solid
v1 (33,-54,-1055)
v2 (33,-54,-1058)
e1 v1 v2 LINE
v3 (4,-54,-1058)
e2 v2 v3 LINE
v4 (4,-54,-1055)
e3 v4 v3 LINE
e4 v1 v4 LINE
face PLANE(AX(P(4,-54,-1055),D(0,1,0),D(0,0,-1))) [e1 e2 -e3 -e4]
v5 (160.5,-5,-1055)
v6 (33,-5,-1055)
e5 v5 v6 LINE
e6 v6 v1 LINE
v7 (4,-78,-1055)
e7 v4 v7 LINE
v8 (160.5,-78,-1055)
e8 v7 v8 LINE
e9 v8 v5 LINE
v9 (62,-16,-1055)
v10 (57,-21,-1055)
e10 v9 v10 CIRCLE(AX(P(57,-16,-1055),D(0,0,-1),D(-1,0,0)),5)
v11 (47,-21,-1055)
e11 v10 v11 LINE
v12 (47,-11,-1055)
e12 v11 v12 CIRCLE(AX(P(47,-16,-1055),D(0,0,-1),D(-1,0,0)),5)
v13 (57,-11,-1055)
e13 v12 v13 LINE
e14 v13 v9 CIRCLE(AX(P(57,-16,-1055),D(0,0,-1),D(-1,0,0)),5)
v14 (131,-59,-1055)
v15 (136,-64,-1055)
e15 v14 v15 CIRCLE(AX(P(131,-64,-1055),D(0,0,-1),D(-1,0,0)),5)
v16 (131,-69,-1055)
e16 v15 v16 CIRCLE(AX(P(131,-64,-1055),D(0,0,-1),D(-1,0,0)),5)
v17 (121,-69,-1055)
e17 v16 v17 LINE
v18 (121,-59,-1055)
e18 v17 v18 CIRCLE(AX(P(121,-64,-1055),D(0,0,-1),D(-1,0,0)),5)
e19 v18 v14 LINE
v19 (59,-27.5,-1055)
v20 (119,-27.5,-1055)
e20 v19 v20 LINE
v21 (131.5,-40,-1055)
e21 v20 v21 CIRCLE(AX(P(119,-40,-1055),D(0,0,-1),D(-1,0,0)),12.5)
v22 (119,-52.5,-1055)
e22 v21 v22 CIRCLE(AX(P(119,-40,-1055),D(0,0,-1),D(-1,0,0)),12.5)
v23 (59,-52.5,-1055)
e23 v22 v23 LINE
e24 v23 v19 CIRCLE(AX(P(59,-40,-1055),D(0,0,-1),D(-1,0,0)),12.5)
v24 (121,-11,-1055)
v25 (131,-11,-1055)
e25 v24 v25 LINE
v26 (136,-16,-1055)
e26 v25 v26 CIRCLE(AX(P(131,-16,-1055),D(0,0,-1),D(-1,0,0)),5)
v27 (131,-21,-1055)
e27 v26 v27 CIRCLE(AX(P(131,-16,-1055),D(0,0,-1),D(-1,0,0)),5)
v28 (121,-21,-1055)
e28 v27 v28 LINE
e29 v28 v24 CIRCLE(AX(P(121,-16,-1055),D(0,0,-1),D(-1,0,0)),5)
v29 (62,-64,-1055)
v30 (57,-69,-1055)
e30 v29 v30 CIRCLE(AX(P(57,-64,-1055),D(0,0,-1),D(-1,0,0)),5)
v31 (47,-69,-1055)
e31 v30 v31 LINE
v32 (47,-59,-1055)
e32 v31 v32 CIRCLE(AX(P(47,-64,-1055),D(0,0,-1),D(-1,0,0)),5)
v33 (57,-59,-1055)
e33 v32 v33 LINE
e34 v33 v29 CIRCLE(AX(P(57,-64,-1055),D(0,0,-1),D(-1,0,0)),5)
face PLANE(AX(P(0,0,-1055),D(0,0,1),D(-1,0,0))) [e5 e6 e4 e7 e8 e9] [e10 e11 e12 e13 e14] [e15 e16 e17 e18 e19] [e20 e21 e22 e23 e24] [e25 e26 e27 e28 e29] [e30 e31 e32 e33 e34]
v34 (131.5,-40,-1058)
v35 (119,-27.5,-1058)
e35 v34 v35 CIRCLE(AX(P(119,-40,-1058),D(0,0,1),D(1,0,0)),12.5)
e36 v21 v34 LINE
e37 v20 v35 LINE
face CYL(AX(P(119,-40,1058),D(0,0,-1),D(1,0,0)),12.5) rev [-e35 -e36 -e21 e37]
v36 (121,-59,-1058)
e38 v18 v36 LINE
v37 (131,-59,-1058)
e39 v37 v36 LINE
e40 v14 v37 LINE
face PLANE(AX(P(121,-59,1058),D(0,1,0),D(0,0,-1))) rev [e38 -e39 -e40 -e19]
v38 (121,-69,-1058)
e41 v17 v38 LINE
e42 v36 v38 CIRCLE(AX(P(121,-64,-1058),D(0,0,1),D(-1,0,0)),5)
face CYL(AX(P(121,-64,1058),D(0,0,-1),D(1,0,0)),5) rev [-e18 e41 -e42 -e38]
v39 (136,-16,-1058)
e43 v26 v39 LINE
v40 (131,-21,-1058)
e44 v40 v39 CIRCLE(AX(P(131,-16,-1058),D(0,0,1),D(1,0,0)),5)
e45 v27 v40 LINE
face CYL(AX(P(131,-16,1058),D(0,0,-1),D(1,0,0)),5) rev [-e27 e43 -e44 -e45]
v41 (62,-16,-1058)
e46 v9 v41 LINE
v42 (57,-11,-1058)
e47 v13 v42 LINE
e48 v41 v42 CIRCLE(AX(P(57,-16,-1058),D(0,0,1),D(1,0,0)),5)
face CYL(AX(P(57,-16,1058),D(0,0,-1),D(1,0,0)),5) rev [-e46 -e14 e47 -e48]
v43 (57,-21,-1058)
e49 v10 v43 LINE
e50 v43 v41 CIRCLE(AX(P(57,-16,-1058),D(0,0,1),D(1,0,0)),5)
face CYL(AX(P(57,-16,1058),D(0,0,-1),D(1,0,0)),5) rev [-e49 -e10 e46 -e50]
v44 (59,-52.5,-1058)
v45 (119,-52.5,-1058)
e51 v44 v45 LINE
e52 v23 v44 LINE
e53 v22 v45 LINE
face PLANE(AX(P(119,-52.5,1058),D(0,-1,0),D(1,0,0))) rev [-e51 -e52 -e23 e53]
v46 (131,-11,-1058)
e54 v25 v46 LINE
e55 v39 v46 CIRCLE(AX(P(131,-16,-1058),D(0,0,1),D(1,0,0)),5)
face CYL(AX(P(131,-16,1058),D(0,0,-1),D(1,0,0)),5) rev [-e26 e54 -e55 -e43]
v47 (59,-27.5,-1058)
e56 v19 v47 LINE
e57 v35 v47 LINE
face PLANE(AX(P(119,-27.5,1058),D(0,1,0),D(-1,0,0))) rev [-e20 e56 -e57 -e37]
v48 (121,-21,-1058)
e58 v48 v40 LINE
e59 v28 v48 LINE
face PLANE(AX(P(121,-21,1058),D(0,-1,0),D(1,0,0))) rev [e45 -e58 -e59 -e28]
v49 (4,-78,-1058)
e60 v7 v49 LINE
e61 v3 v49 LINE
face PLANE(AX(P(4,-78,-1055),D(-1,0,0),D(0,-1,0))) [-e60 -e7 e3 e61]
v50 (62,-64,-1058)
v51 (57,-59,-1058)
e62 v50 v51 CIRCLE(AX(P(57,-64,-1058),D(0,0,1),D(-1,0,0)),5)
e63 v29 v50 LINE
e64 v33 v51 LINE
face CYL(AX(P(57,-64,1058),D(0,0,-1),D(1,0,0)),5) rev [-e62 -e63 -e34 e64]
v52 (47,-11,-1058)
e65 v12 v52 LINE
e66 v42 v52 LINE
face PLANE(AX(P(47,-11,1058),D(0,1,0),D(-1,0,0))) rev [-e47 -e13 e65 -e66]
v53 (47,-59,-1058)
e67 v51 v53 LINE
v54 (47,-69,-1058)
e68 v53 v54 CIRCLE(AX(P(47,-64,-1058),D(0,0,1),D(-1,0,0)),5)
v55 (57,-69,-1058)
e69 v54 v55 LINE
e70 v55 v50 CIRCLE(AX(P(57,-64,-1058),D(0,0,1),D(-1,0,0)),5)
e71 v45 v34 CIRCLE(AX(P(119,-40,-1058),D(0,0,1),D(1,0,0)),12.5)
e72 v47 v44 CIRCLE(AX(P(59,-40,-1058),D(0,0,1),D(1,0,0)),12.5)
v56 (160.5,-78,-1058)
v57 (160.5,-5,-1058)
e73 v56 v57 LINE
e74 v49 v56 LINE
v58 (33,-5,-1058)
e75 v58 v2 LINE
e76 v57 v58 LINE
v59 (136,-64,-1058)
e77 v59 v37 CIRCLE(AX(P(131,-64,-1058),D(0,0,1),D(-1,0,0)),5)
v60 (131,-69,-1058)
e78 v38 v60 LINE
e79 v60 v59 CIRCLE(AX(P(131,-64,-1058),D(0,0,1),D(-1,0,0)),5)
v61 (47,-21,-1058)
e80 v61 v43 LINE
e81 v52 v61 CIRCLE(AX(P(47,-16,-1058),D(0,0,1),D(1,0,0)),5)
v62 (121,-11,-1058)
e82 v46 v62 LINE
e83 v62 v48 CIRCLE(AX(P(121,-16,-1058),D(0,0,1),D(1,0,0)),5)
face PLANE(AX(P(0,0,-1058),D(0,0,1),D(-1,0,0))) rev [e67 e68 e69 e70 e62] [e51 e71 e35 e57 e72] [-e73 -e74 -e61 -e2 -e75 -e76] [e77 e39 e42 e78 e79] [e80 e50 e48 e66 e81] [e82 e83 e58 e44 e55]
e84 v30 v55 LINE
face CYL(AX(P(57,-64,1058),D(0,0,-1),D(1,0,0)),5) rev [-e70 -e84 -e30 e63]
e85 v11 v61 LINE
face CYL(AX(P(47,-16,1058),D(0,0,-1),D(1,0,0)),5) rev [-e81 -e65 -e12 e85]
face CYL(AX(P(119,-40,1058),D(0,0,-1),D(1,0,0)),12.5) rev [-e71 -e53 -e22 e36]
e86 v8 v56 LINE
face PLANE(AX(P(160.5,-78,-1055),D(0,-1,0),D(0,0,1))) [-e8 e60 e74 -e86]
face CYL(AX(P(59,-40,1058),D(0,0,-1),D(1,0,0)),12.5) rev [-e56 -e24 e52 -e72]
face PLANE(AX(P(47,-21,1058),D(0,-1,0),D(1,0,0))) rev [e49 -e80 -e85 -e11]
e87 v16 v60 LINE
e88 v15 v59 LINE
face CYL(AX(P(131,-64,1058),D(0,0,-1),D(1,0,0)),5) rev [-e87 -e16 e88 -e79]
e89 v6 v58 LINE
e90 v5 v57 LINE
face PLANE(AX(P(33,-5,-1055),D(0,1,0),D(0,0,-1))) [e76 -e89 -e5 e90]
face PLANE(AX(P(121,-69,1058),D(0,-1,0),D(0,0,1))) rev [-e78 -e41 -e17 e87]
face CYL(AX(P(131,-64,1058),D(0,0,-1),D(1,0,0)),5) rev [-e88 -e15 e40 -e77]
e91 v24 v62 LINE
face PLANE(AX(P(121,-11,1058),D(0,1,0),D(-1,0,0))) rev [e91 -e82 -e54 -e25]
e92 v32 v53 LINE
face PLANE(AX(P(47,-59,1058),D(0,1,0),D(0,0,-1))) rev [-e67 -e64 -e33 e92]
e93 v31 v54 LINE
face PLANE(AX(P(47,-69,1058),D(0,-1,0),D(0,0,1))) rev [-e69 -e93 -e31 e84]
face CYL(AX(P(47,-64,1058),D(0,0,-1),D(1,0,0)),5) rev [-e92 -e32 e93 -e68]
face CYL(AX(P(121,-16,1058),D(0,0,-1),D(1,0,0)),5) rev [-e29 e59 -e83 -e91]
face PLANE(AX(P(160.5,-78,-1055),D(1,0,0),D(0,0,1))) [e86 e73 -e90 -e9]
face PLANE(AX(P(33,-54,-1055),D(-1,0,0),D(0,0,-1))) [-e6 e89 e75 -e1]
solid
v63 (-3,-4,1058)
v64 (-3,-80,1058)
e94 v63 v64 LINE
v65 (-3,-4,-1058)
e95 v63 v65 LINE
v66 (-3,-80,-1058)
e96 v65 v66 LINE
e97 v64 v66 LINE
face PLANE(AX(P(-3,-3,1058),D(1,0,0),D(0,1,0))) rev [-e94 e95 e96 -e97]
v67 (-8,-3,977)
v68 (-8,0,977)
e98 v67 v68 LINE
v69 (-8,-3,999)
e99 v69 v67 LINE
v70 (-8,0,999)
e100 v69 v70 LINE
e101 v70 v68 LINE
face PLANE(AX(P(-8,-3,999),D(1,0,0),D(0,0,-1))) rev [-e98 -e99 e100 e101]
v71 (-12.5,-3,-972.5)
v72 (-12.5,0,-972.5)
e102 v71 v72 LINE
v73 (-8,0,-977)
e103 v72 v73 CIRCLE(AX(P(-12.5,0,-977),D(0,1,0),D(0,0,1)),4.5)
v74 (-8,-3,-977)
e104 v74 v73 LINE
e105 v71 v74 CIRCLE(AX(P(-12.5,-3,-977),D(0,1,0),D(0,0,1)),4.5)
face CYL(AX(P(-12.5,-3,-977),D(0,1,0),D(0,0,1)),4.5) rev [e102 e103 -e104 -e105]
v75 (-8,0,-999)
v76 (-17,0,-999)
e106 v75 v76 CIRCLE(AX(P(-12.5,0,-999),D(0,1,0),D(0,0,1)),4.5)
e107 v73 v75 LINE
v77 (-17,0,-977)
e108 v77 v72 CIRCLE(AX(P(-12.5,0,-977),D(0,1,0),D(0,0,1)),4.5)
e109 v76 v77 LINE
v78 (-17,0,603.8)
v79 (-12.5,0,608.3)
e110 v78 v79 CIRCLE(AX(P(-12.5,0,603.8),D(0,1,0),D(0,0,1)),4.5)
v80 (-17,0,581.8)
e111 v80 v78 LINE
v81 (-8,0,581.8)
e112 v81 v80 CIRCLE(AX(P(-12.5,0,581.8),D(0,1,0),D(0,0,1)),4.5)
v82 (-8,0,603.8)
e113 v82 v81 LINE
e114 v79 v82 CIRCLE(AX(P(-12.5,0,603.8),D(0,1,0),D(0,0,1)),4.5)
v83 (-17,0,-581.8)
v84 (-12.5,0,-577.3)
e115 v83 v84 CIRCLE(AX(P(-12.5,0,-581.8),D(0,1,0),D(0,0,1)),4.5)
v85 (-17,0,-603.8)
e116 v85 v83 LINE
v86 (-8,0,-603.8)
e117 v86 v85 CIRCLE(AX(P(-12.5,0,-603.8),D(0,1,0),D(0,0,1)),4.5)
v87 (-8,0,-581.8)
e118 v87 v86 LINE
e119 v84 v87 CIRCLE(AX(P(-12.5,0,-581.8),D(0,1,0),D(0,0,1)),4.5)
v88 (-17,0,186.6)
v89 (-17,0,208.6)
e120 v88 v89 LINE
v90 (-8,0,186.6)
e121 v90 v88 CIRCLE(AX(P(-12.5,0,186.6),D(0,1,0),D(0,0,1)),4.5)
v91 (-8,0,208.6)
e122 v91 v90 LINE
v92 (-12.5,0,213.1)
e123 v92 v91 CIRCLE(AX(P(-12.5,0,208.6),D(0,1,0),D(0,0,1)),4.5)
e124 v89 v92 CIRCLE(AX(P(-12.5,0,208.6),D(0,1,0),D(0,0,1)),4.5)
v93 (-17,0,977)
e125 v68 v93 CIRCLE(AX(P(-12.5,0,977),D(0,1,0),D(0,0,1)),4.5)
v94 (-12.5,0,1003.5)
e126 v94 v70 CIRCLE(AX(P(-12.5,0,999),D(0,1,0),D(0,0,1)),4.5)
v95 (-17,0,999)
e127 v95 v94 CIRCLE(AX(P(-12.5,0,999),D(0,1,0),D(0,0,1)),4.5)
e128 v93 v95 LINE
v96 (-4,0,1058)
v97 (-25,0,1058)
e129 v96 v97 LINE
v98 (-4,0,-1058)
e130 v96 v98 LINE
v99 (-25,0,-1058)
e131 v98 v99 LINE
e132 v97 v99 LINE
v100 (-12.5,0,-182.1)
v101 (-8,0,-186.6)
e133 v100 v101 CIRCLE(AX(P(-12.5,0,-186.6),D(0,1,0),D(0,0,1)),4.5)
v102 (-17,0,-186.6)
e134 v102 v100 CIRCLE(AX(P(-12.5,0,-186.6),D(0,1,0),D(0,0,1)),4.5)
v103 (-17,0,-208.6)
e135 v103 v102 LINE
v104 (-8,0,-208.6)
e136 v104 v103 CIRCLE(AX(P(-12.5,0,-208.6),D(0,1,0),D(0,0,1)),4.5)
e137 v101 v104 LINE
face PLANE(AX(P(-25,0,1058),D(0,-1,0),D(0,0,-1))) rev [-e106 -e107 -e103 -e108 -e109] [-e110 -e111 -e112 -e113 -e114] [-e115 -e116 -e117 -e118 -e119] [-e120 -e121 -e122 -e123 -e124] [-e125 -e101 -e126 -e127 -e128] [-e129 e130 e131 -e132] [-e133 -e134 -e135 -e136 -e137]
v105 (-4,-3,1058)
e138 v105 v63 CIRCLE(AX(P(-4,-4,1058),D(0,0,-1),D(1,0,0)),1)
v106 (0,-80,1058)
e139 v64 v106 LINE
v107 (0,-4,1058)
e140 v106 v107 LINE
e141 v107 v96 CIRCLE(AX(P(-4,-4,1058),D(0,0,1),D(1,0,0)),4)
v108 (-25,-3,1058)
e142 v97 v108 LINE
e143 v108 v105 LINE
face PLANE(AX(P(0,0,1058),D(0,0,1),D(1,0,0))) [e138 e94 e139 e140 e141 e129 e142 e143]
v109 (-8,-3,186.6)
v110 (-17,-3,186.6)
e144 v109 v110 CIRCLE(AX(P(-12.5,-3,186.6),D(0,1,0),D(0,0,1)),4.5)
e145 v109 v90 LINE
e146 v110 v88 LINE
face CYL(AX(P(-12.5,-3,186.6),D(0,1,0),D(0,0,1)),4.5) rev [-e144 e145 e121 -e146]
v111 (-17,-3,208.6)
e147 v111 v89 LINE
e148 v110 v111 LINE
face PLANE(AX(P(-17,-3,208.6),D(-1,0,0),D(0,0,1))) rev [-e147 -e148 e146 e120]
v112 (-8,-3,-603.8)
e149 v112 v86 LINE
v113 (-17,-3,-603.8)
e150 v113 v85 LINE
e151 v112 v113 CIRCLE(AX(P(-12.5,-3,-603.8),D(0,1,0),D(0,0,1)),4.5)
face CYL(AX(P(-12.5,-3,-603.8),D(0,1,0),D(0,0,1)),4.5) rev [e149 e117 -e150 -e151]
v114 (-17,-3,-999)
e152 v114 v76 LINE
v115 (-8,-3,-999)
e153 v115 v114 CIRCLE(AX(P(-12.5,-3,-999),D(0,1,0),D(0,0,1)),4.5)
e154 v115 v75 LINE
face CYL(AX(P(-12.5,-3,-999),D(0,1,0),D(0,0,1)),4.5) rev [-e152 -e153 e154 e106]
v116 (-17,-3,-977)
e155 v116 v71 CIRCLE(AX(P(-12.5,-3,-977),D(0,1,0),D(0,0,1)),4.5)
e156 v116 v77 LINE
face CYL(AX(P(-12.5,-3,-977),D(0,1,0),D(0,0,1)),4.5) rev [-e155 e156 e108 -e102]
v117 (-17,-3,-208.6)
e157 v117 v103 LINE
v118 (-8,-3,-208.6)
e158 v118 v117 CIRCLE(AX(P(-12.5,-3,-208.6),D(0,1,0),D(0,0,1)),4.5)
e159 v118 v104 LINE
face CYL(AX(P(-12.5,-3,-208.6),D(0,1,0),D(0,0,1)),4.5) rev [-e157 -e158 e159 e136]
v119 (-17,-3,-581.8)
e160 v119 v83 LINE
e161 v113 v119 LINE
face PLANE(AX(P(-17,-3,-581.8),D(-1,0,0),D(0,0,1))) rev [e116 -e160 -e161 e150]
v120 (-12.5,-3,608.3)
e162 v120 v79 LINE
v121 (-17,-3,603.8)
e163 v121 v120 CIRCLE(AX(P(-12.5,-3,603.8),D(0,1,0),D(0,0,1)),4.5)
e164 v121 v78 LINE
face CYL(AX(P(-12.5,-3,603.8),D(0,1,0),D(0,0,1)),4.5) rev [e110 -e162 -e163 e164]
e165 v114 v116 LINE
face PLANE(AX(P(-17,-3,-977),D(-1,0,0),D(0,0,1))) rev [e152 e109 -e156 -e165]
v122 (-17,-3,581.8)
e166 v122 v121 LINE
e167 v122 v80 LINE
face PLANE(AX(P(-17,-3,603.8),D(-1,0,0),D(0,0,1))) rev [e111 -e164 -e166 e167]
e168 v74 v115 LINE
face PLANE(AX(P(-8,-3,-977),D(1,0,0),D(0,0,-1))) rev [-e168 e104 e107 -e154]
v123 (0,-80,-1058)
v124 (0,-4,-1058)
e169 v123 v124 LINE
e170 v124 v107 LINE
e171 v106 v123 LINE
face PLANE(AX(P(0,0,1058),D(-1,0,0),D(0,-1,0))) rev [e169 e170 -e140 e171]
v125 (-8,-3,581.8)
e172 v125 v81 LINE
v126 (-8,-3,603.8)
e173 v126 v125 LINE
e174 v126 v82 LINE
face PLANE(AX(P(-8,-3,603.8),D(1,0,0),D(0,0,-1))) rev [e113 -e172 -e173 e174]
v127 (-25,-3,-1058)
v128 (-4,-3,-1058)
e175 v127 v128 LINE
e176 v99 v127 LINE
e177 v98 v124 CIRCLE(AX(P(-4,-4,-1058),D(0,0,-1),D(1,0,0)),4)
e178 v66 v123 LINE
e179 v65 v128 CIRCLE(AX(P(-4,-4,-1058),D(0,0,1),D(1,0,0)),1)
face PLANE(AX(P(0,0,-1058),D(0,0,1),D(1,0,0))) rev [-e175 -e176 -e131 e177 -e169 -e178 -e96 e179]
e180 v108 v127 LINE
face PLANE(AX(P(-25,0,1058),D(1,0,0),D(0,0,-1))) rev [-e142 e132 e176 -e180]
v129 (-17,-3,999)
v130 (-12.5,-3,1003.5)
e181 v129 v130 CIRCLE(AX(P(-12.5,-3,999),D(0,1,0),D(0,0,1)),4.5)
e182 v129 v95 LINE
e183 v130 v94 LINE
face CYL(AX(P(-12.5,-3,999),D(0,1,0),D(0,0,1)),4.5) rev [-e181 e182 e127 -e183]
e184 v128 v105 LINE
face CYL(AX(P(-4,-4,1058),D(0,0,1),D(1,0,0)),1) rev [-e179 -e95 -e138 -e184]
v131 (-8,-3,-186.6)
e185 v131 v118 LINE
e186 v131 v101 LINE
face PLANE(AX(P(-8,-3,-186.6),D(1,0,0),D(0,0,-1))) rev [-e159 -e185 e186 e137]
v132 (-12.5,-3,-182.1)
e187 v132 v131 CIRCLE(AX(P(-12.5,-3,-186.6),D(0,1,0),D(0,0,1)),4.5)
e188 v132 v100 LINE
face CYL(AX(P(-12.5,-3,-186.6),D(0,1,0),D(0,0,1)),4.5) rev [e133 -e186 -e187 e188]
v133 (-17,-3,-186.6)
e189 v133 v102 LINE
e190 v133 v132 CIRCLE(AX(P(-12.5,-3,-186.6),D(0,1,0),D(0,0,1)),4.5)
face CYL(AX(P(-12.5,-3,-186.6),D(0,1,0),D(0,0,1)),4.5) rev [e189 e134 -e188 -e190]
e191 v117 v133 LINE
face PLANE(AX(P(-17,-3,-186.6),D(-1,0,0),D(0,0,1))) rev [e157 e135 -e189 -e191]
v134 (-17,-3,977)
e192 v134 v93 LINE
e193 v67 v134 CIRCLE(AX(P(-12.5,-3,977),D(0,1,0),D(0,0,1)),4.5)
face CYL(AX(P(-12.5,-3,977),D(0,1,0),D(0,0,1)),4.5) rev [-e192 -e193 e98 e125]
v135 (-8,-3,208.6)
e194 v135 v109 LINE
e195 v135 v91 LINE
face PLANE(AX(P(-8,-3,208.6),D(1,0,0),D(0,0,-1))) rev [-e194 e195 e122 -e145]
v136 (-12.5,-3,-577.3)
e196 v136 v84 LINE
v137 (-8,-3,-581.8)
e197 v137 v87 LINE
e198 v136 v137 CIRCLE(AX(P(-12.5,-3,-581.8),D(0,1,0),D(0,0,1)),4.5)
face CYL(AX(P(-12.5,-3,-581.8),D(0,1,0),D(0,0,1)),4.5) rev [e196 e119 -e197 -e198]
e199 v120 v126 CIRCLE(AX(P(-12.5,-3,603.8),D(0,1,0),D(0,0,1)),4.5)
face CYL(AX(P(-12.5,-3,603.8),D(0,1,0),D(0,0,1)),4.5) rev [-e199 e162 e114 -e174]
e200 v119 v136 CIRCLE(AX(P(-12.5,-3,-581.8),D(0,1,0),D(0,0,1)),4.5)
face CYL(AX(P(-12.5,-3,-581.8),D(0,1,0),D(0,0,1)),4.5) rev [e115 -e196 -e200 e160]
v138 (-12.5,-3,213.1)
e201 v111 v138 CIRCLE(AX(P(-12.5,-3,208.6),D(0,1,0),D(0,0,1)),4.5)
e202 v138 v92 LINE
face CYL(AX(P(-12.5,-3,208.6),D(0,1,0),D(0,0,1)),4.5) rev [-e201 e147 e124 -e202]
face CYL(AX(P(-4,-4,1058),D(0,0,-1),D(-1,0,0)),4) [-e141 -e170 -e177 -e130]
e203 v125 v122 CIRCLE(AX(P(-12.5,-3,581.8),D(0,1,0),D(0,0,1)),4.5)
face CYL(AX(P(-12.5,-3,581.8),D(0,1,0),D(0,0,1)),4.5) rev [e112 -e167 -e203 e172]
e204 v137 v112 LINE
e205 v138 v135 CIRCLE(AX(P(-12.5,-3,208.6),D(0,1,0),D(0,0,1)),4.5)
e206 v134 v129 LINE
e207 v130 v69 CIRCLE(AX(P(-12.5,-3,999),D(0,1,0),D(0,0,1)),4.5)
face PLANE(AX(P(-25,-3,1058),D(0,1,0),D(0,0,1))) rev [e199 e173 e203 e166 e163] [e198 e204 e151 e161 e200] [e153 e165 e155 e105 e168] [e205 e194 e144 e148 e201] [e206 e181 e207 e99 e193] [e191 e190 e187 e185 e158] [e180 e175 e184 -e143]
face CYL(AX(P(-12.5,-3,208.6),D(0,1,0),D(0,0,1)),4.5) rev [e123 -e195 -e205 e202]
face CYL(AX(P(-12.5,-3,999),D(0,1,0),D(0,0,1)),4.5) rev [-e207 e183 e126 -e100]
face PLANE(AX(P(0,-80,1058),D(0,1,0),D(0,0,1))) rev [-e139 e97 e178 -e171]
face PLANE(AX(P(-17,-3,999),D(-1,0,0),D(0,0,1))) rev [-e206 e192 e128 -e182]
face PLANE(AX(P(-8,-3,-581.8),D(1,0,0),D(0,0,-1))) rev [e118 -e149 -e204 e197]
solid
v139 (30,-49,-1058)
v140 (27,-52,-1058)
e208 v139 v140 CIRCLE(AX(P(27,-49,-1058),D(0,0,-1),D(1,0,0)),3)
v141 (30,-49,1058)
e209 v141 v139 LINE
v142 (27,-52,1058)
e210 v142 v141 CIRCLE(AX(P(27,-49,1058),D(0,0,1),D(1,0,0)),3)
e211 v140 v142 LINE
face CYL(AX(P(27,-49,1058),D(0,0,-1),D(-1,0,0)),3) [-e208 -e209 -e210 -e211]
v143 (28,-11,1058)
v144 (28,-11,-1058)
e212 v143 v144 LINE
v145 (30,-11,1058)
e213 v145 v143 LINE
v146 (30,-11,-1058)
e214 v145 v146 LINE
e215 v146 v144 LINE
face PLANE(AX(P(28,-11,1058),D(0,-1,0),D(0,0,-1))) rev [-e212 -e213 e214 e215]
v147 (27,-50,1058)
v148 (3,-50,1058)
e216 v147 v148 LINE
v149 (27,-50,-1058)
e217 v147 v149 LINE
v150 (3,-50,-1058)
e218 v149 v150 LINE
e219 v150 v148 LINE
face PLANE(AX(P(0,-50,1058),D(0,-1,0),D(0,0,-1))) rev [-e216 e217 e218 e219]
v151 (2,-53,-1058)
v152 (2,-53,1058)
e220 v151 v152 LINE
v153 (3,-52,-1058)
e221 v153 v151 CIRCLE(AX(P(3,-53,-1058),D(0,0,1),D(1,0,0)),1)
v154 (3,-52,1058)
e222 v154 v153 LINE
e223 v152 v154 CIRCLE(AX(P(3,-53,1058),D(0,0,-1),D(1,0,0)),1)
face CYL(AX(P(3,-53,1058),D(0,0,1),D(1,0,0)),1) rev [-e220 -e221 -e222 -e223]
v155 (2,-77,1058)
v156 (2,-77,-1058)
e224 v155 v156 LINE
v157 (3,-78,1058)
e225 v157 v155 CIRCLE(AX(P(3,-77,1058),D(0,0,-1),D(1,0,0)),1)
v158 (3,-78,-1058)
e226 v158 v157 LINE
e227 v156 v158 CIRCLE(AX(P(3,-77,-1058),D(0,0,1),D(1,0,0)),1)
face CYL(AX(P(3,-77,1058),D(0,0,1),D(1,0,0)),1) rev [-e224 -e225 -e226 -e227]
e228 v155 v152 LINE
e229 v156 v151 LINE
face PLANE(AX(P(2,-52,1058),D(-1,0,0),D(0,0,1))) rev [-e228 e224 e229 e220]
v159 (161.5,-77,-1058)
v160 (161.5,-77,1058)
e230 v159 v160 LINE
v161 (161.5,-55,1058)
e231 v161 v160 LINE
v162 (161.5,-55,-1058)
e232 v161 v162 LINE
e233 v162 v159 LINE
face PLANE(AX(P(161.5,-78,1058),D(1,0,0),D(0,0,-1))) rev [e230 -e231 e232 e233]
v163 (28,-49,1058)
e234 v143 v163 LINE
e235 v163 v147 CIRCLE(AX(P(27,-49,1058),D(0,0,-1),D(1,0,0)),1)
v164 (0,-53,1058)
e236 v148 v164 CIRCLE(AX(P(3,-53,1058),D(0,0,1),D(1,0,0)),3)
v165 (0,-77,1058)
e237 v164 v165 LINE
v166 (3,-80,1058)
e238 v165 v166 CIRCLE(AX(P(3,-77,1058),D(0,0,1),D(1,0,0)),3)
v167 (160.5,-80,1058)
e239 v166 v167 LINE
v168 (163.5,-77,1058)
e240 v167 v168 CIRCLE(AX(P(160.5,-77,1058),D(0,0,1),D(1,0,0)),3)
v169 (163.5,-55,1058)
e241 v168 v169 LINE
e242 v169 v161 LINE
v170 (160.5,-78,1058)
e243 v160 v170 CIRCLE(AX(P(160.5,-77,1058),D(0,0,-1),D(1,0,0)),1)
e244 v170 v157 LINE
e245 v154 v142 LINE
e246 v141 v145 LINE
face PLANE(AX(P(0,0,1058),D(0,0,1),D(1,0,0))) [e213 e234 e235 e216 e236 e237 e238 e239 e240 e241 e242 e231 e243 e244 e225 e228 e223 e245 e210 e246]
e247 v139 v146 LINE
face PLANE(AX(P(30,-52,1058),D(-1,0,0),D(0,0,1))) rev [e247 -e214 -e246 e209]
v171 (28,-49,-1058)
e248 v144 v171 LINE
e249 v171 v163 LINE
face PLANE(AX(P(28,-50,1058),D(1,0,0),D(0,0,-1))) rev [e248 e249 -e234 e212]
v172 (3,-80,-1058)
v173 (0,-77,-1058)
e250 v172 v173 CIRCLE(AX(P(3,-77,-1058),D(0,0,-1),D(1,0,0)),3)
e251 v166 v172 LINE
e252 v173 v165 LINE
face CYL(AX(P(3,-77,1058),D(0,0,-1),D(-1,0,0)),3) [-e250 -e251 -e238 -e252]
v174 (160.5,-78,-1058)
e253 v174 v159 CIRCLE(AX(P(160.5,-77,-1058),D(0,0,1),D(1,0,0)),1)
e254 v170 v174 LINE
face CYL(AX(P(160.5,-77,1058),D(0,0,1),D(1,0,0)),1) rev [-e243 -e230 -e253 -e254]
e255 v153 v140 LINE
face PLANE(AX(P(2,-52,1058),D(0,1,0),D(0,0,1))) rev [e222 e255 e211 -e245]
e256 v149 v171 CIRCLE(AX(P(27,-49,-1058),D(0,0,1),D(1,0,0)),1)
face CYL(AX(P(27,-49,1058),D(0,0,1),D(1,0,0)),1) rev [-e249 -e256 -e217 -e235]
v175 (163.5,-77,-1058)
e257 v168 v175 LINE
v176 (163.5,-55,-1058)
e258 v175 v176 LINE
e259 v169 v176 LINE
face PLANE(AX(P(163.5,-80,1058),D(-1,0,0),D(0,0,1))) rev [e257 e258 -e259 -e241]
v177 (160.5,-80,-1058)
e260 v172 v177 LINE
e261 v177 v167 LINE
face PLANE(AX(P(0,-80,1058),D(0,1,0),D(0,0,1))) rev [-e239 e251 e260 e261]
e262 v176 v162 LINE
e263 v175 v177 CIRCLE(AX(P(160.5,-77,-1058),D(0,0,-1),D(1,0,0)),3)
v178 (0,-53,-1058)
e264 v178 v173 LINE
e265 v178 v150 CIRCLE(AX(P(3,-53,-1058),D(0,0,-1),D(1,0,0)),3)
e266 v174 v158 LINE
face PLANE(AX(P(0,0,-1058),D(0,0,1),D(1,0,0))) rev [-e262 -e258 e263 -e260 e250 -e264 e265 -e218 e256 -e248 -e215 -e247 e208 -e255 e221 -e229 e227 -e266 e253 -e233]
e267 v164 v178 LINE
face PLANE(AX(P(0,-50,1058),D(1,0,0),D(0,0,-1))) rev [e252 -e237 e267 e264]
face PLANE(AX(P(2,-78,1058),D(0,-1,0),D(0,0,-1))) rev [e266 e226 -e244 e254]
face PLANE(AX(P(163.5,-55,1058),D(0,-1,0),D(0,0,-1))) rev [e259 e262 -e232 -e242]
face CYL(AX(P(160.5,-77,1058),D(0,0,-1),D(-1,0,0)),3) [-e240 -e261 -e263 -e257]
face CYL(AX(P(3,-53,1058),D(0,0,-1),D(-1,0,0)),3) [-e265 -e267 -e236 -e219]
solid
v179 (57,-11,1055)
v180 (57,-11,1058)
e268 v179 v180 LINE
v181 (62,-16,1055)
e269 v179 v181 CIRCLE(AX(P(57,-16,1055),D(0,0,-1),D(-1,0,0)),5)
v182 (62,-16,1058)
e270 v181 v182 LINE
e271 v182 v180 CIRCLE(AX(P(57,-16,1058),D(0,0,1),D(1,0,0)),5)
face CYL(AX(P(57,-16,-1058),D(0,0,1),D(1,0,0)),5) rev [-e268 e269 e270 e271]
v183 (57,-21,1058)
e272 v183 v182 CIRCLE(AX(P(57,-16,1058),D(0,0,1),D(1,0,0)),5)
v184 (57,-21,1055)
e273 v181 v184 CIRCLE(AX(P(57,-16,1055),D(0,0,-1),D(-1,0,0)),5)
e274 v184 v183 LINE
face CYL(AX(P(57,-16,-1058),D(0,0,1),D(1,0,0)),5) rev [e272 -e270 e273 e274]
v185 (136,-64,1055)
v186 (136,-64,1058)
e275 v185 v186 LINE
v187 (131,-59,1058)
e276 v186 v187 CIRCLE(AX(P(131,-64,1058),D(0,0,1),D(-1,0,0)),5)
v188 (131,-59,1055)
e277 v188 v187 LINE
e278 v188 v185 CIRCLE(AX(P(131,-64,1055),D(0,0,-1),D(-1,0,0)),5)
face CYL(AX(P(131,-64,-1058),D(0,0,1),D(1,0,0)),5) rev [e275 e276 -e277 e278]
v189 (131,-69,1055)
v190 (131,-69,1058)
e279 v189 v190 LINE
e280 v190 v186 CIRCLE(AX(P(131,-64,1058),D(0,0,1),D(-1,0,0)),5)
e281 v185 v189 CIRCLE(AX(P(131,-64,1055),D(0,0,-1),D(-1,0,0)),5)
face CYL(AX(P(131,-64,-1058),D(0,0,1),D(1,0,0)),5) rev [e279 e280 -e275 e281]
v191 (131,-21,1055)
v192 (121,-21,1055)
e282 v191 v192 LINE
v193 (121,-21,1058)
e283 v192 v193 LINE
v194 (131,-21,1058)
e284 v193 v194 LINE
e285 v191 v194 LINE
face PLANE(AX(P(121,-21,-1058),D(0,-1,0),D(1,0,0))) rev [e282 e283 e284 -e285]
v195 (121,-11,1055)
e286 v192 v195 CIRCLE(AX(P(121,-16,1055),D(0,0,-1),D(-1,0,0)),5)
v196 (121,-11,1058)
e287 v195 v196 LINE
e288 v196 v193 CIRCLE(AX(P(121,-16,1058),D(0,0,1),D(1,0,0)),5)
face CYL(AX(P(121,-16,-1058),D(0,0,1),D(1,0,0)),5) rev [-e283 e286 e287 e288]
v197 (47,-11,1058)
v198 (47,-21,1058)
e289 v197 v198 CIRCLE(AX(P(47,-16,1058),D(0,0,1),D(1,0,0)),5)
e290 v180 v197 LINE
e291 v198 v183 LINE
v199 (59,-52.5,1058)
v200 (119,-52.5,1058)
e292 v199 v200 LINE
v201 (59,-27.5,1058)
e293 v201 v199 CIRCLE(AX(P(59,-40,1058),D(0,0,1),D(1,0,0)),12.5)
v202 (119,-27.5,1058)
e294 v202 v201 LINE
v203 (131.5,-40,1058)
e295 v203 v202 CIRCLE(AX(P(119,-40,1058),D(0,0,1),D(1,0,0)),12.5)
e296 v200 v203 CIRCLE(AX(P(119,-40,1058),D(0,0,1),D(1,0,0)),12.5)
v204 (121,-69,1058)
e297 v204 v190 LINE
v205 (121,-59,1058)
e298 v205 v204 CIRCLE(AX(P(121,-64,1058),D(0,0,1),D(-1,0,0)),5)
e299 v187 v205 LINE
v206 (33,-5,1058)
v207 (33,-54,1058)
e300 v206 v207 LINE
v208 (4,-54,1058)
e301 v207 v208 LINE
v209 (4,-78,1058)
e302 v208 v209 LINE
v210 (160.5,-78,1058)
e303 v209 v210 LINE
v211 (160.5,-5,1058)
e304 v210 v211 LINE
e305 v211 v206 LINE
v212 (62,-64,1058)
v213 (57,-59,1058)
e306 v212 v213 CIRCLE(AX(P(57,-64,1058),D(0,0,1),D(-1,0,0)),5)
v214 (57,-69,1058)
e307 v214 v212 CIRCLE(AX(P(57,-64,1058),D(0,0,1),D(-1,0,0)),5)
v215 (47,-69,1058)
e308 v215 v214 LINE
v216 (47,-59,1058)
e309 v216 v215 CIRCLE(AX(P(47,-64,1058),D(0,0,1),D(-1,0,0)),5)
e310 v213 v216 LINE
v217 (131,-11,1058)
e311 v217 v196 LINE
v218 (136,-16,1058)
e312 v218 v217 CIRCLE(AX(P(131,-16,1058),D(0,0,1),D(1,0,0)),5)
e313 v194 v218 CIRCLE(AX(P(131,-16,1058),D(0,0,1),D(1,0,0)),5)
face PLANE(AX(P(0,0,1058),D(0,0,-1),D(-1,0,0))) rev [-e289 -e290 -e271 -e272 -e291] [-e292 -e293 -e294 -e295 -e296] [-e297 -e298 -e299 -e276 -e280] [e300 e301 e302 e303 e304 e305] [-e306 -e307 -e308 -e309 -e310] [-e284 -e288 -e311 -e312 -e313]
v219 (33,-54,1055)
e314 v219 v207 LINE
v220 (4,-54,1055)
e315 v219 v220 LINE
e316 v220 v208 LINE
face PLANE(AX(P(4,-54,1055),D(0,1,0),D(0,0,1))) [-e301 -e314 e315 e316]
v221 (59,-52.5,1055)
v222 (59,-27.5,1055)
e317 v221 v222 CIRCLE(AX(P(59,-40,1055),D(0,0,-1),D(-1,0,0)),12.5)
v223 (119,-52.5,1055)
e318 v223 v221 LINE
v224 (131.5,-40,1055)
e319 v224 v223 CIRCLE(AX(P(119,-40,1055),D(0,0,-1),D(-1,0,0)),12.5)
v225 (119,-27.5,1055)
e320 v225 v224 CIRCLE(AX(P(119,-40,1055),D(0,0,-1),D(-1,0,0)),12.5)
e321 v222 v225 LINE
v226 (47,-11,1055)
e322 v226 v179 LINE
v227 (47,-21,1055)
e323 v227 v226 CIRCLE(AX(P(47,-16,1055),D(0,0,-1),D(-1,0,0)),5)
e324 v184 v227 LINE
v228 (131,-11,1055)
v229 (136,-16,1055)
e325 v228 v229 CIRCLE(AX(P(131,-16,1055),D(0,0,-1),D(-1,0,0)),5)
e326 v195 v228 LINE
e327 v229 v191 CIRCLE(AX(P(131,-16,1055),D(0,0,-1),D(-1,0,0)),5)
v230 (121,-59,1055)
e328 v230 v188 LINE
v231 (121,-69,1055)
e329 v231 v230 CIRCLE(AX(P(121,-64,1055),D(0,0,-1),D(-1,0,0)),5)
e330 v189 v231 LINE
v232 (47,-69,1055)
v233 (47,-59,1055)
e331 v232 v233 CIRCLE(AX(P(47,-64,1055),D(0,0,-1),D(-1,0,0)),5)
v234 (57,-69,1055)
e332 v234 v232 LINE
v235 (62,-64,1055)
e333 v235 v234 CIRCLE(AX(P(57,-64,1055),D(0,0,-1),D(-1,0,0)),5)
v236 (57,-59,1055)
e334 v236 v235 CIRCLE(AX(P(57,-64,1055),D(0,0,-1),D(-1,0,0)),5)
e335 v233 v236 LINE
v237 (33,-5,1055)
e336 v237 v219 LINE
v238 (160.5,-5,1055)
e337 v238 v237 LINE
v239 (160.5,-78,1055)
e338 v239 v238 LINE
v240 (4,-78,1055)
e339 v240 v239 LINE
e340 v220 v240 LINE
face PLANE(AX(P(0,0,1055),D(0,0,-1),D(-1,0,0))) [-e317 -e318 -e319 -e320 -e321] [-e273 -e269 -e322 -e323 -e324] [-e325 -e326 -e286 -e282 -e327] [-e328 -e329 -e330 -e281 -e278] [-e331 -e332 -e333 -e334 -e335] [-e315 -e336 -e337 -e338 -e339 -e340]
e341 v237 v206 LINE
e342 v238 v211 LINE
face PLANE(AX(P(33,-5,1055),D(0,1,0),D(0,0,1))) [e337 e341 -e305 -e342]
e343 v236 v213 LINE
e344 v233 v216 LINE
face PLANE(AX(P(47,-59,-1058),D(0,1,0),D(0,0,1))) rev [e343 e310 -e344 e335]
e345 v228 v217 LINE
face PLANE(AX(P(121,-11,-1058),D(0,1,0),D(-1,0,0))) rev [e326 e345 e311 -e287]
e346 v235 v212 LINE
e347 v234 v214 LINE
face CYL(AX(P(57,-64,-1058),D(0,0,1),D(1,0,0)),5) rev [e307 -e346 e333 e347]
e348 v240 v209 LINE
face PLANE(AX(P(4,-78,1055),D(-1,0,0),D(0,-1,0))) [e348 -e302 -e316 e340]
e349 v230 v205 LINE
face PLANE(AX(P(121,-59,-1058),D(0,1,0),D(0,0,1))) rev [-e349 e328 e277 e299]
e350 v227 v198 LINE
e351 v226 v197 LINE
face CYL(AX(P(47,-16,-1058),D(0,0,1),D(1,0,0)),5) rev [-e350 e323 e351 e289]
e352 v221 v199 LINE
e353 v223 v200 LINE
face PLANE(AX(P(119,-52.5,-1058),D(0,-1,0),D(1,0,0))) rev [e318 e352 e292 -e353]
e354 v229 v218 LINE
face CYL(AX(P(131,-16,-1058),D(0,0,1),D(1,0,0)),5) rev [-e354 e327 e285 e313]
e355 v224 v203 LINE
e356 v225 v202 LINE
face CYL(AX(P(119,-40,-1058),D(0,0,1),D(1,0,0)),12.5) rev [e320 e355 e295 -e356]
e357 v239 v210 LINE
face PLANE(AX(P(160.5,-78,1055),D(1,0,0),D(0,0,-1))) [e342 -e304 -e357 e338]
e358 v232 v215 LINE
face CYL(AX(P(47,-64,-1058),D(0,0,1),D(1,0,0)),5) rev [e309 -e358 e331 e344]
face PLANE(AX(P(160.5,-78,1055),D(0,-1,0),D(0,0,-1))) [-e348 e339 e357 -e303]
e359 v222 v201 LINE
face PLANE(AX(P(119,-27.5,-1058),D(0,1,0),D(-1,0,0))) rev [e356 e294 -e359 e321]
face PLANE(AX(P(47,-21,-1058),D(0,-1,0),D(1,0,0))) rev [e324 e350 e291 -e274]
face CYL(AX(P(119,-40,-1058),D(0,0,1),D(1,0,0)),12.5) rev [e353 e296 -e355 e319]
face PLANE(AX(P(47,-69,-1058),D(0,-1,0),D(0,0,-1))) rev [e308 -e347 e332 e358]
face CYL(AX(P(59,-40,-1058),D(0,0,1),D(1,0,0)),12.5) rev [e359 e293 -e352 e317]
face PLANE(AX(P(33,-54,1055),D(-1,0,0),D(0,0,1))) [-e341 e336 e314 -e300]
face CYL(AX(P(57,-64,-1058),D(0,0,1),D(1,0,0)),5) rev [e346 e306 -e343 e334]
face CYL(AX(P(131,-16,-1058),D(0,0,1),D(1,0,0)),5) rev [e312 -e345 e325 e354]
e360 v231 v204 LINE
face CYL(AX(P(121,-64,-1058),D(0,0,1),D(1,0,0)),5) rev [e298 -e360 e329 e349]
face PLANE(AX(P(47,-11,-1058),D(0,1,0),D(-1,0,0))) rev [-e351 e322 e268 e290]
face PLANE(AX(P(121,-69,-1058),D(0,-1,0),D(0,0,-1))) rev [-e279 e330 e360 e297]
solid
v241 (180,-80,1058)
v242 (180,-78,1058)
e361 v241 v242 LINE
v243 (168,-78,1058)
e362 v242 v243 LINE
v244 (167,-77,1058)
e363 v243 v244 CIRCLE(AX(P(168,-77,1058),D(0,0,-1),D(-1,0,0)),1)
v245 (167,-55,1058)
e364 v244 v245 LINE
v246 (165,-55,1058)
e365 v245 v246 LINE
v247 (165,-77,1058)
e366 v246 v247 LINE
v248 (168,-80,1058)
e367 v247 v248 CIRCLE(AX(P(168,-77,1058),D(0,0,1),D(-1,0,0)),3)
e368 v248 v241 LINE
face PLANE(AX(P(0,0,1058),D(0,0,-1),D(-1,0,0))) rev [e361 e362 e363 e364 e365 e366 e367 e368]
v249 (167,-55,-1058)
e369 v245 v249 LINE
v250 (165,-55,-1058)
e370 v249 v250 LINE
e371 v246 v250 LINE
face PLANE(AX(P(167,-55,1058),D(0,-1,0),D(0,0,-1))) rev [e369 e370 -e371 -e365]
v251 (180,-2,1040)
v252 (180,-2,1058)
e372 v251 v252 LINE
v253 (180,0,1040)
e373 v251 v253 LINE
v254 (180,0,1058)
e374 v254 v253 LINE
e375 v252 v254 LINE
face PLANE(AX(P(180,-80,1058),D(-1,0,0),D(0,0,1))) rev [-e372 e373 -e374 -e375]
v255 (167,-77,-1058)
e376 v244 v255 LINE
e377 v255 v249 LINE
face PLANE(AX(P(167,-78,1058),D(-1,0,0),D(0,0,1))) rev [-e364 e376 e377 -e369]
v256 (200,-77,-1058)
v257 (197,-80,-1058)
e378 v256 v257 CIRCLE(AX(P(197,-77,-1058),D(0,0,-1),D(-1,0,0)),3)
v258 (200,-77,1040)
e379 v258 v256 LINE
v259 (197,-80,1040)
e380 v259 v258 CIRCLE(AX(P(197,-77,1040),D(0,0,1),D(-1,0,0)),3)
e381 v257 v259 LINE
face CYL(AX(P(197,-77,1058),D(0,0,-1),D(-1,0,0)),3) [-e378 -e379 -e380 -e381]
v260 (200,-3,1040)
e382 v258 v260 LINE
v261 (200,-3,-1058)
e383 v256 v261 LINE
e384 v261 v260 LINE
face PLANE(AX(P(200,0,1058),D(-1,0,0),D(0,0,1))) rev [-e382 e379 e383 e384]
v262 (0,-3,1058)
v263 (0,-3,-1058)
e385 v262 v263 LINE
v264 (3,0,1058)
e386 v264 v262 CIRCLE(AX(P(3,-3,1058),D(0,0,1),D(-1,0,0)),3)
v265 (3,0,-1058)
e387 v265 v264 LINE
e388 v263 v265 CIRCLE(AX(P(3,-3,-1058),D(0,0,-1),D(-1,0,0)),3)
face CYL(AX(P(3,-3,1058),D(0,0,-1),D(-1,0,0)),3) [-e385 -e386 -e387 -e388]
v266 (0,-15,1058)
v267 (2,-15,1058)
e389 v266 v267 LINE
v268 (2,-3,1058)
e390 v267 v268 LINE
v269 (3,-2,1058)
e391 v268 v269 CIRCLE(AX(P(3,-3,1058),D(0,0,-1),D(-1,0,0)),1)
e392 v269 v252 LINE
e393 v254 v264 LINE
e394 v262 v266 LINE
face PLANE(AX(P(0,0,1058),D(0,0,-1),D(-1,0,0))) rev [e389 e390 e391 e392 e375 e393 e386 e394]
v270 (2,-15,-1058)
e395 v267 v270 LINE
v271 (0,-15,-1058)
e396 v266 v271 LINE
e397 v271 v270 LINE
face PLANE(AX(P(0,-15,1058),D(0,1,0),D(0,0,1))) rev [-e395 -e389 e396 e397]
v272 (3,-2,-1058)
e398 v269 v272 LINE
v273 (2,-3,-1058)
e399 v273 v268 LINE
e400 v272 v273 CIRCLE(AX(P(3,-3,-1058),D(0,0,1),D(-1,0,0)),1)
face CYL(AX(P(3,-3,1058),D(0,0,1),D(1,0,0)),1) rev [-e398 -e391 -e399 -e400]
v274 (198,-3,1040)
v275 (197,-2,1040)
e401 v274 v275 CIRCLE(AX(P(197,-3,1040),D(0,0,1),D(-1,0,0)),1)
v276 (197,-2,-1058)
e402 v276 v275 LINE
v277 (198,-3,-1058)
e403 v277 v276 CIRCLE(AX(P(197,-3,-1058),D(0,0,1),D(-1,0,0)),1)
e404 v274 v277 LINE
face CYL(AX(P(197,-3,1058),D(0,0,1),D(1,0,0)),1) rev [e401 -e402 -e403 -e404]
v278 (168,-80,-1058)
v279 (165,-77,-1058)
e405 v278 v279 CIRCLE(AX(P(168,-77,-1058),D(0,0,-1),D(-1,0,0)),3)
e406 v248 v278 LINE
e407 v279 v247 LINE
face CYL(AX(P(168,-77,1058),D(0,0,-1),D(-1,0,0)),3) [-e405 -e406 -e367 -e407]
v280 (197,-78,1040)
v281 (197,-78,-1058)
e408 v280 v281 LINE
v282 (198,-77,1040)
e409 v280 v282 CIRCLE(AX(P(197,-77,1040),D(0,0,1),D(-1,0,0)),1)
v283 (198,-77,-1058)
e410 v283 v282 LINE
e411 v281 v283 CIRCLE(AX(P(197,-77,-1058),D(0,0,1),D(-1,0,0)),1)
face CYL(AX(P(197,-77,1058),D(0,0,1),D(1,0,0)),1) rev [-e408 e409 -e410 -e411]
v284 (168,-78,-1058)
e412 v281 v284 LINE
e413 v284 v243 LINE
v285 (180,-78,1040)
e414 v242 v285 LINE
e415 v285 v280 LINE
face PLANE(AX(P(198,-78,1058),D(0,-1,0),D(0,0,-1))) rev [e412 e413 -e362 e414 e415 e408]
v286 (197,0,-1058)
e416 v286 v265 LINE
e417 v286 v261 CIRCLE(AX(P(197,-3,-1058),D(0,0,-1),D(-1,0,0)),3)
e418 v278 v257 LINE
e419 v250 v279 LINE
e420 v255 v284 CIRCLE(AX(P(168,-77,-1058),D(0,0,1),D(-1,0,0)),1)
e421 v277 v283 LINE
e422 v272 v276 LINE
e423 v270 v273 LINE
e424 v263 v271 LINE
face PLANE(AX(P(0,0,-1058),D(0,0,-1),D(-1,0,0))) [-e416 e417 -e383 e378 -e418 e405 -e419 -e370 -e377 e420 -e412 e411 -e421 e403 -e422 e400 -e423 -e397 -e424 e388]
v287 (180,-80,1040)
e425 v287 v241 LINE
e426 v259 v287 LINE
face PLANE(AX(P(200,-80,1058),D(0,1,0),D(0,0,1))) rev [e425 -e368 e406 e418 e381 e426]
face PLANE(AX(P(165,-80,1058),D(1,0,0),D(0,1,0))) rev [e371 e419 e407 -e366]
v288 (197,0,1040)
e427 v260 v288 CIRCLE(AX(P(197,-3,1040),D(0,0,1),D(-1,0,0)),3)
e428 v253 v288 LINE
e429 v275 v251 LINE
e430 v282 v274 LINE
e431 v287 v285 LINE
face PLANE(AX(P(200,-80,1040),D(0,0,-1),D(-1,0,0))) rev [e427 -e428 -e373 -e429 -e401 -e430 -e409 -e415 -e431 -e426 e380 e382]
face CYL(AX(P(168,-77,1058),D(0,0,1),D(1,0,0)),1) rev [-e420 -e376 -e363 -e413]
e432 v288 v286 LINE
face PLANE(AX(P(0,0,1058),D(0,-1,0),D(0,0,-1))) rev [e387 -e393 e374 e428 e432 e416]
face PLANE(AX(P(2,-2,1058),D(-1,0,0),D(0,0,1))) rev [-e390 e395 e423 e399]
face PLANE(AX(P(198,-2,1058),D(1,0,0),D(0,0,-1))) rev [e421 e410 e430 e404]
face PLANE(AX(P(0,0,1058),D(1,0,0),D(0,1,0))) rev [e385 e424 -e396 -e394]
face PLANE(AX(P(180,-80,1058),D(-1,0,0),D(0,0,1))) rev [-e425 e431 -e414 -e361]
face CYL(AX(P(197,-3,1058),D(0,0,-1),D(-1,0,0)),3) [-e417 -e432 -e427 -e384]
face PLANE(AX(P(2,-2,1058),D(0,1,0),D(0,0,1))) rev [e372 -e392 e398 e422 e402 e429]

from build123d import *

# Parameters (mm, degrees)
EXTRUDE_1_DEPTH             = 1058
EXTRUDE_2_DEPTH             = 1058
EXTRUDE_2_2_DEPTH           = 1058
EXTRUDE_3_DEPTH             = 3
FILLET_1_R                  = 4
FILLET_2_R                  = 1
FILLET_3_R                  = 1
FILLET_4_R                  = 1
FILLET_5_R                  = 3
FILLET_6_R                  = 3
CUT_EXTRUDE_1_DEPTH         = 2127.935824138
CUT_EXTRUDE_3487_DEPTH      = 3
CUT_EXTRUDE_3708_DEPTH      = 1080.705515407
CUT_EXTRUDE_3708_DEPTH_BACK = 1080.705515407
SKETCH_6_W                  = 20
SKETCH_6_H                  = 18


with BuildPart() as part:
    # 草图1 → 凸台-拉伸1 (new, symmetric)
    with BuildSketch(Plane.XY):
        Polygon((-25, 0), (0, 0), (0, -80), (-3, -80), (-3, -3), (-25, -3), align=None)
    extrude(amount=EXTRUDE_1_DEPTH, both=True)

    # 圆角1
    fillet_1_edges = [part.edges().sort_by_distance(p)[0] for p in [
        (0, 0, 0),
    ]]
    fillet(fillet_1_edges, radius=FILLET_1_R)

    # 圆角2
    fillet_2_edges = [part.edges().sort_by_distance(p)[0] for p in [
        (-3, -3, 0),
    ]]
    fillet(fillet_2_edges, radius=FILLET_2_R)

    # 草图7 → Cut-Extrude 3487 (cut)
    with BuildSketch(Plane(origin=(0, 0, 0), x_dir=(1, 0, 0), z_dir=(0, 1, 0))):
        with BuildLine():
            Line((-17, 977), (-17, 999))
            ThreePointArc((-17, 999), (-12.5, 1003.5), (-8, 999))
            Line((-8, 999), (-8, 977))
            ThreePointArc((-8, 977), (-12.5, 972.5), (-17, 977))
        make_face()
        with BuildLine():
            Line((-17, 581.8), (-17, 603.8))
            ThreePointArc((-17, 603.8), (-12.5, 608.3), (-8, 603.8))
            Line((-8, 603.8), (-8, 581.8))
            ThreePointArc((-8, 581.8), (-12.5, 577.3), (-17, 581.8))
        make_face()
        with BuildLine():
            Line((-17, 186.6), (-17, 208.6))
            ThreePointArc((-17, 208.6), (-12.5, 213.1), (-8, 208.6))
            Line((-8, 208.6), (-8, 186.6))
            ThreePointArc((-8, 186.6), (-12.5, 182.1), (-17, 186.6))
        make_face()
        with BuildLine():
            Line((-17, -208.6), (-17, -186.6))
            ThreePointArc((-17, -186.6), (-12.5, -182.1), (-8, -186.6))
            Line((-8, -186.6), (-8, -208.6))
            ThreePointArc((-8, -208.6), (-12.5, -213.1), (-17, -208.6))
        make_face()
        with BuildLine():
            Line((-17, -603.8), (-17, -581.8))
            ThreePointArc((-17, -581.8), (-12.5, -577.3), (-8, -581.8))
            Line((-8, -581.8), (-8, -603.8))
            ThreePointArc((-8, -603.8), (-12.5, -608.3), (-17, -603.8))
        make_face()
        with BuildLine():
            Line((-17, -999), (-17, -977))
            ThreePointArc((-17, -977), (-12.5, -972.5), (-8, -977))
            Line((-8, -977), (-8, -999))
            ThreePointArc((-8, -999), (-12.5, -1003.5), (-17, -999))
        make_face()
    extrude(amount=-CUT_EXTRUDE_3487_DEPTH, mode=Mode.SUBTRACT)


with BuildPart() as body_2:
    # 草图2 → 凸台-拉伸2 (new, symmetric)
    with BuildSketch(Plane.XY):
        Polygon((0, 0), (0, -15), (2, -15), (2, -2), (198, -2), (198, -78), (167, -78), (167, -55), (165, -55), (165, -80), (200, -80), (200, 0), align=None)
    extrude(amount=EXTRUDE_2_DEPTH, both=True)

    # 圆角3
    fillet_3_edges = [body_2.edges().sort_by_distance(p)[0] for p in [
        (167, -78, 0),
        (198, -78, 0),
        (198, -2, 0),
        (2, -2, 0),
    ]]
    fillet(fillet_3_edges, radius=FILLET_3_R)

    # 圆角5
    fillet_5_edges = [body_2.edges().sort_by_distance(p)[0] for p in [
        (200, 0, 0),
        (200, -80, 0),
        (165, -80, 0),
        (0, 0, 0),
    ]]
    fillet(fillet_5_edges, radius=FILLET_5_R)

    # 草图6 → Cut-Extrude 3708 (cut, two sides: drawn at the far end of the back side and taken through both)
    with BuildSketch(Plane(origin=(0, 0, 0), x_dir=(1, 0, 0), z_dir=(0, 1, 0)).offset(-CUT_EXTRUDE_3708_DEPTH_BACK)):
        with Locations((190, -1049)):
            Rectangle(SKETCH_6_W, SKETCH_6_H)
    extrude(amount=CUT_EXTRUDE_3708_DEPTH + CUT_EXTRUDE_3708_DEPTH_BACK, mode=Mode.SUBTRACT)


with BuildPart() as body_3:
    # 草图2 → Extrude 2 2 (new, symmetric)
    with BuildSketch(Plane.XY):
        Polygon((0, -50), (0, -80), (163.5, -80), (163.5, -55), (161.5, -55), (161.5, -78), (2, -78), (2, -52), (30, -52), (30, -11), (28, -11), (28, -50), align=None)
    extrude(amount=EXTRUDE_2_2_DEPTH, both=True)

    # 圆角4
    fillet_4_edges = [body_3.edges().sort_by_distance(p)[0] for p in [
        (28, -50, 0),
        (2, -52, 0),
        (2, -78, 0),
        (161.5, -78, 0),
    ]]
    fillet(fillet_4_edges, radius=FILLET_4_R)

    # 圆角6
    fillet_6_edges = [body_3.edges().sort_by_distance(p)[0] for p in [
        (30, -52, 0),
        (163.5, -80, 0),
        (0, -80, 0),
        (0, -50, 0),
    ]]
    fillet(fillet_6_edges, radius=FILLET_6_R)


with BuildPart() as body_4:
    # 草图3 → 凸台-拉伸3 (new body)
    with BuildSketch(Plane.XY.offset(1058)):
        Polygon((160.5, -78), (160.5, -5), (33, -5), (33, -54), (4, -54), (4, -78), align=None)
    extrude(amount=-EXTRUDE_3_DEPTH)

    # 草图5 → 切除-拉伸1 (cut, through all)
    with BuildSketch(Plane.XY.offset(1058)):
        with BuildLine():
            Line((47, -11), (57, -11))
            ThreePointArc((57, -11), (62, -16), (57, -21))
            Line((57, -21), (47, -21))
            ThreePointArc((47, -21), (42, -16), (47, -11))
        make_face()
        with BuildLine():
            Line((47, -69), (57, -69))
            ThreePointArc((57, -69), (62, -64), (57, -59))
            Line((57, -59), (47, -59))
            ThreePointArc((47, -59), (42, -64), (47, -69))
        make_face()
        with BuildLine():
            Line((121, -11), (131, -11))
            ThreePointArc((131, -11), (136, -16), (131, -21))
            Line((131, -21), (121, -21))
            ThreePointArc((121, -21), (116, -16), (121, -11))
        make_face()
        with BuildLine():
            Line((121, -69), (131, -69))
            ThreePointArc((131, -69), (136, -64), (131, -59))
            Line((131, -59), (121, -59))
            ThreePointArc((121, -59), (116, -64), (121, -69))
        make_face()
        with BuildLine():
            Line((119, -52.5), (59, -52.5))
            ThreePointArc((59, -52.5), (46.5, -40), (59, -27.5))
            Line((59, -27.5), (119, -27.5))
            ThreePointArc((119, -27.5), (131.5, -40), (119, -52.5))
        make_face()
    extrude(amount=-CUT_EXTRUDE_1_DEPTH, mode=Mode.SUBTRACT)


with BuildPart() as body_5:
    # 镜向1: mirrored copy
    add(body_4.part.mirror(Plane.XY))


solid = Compound([part.part, body_2.part, body_3.part, body_4.part, body_5.part])
